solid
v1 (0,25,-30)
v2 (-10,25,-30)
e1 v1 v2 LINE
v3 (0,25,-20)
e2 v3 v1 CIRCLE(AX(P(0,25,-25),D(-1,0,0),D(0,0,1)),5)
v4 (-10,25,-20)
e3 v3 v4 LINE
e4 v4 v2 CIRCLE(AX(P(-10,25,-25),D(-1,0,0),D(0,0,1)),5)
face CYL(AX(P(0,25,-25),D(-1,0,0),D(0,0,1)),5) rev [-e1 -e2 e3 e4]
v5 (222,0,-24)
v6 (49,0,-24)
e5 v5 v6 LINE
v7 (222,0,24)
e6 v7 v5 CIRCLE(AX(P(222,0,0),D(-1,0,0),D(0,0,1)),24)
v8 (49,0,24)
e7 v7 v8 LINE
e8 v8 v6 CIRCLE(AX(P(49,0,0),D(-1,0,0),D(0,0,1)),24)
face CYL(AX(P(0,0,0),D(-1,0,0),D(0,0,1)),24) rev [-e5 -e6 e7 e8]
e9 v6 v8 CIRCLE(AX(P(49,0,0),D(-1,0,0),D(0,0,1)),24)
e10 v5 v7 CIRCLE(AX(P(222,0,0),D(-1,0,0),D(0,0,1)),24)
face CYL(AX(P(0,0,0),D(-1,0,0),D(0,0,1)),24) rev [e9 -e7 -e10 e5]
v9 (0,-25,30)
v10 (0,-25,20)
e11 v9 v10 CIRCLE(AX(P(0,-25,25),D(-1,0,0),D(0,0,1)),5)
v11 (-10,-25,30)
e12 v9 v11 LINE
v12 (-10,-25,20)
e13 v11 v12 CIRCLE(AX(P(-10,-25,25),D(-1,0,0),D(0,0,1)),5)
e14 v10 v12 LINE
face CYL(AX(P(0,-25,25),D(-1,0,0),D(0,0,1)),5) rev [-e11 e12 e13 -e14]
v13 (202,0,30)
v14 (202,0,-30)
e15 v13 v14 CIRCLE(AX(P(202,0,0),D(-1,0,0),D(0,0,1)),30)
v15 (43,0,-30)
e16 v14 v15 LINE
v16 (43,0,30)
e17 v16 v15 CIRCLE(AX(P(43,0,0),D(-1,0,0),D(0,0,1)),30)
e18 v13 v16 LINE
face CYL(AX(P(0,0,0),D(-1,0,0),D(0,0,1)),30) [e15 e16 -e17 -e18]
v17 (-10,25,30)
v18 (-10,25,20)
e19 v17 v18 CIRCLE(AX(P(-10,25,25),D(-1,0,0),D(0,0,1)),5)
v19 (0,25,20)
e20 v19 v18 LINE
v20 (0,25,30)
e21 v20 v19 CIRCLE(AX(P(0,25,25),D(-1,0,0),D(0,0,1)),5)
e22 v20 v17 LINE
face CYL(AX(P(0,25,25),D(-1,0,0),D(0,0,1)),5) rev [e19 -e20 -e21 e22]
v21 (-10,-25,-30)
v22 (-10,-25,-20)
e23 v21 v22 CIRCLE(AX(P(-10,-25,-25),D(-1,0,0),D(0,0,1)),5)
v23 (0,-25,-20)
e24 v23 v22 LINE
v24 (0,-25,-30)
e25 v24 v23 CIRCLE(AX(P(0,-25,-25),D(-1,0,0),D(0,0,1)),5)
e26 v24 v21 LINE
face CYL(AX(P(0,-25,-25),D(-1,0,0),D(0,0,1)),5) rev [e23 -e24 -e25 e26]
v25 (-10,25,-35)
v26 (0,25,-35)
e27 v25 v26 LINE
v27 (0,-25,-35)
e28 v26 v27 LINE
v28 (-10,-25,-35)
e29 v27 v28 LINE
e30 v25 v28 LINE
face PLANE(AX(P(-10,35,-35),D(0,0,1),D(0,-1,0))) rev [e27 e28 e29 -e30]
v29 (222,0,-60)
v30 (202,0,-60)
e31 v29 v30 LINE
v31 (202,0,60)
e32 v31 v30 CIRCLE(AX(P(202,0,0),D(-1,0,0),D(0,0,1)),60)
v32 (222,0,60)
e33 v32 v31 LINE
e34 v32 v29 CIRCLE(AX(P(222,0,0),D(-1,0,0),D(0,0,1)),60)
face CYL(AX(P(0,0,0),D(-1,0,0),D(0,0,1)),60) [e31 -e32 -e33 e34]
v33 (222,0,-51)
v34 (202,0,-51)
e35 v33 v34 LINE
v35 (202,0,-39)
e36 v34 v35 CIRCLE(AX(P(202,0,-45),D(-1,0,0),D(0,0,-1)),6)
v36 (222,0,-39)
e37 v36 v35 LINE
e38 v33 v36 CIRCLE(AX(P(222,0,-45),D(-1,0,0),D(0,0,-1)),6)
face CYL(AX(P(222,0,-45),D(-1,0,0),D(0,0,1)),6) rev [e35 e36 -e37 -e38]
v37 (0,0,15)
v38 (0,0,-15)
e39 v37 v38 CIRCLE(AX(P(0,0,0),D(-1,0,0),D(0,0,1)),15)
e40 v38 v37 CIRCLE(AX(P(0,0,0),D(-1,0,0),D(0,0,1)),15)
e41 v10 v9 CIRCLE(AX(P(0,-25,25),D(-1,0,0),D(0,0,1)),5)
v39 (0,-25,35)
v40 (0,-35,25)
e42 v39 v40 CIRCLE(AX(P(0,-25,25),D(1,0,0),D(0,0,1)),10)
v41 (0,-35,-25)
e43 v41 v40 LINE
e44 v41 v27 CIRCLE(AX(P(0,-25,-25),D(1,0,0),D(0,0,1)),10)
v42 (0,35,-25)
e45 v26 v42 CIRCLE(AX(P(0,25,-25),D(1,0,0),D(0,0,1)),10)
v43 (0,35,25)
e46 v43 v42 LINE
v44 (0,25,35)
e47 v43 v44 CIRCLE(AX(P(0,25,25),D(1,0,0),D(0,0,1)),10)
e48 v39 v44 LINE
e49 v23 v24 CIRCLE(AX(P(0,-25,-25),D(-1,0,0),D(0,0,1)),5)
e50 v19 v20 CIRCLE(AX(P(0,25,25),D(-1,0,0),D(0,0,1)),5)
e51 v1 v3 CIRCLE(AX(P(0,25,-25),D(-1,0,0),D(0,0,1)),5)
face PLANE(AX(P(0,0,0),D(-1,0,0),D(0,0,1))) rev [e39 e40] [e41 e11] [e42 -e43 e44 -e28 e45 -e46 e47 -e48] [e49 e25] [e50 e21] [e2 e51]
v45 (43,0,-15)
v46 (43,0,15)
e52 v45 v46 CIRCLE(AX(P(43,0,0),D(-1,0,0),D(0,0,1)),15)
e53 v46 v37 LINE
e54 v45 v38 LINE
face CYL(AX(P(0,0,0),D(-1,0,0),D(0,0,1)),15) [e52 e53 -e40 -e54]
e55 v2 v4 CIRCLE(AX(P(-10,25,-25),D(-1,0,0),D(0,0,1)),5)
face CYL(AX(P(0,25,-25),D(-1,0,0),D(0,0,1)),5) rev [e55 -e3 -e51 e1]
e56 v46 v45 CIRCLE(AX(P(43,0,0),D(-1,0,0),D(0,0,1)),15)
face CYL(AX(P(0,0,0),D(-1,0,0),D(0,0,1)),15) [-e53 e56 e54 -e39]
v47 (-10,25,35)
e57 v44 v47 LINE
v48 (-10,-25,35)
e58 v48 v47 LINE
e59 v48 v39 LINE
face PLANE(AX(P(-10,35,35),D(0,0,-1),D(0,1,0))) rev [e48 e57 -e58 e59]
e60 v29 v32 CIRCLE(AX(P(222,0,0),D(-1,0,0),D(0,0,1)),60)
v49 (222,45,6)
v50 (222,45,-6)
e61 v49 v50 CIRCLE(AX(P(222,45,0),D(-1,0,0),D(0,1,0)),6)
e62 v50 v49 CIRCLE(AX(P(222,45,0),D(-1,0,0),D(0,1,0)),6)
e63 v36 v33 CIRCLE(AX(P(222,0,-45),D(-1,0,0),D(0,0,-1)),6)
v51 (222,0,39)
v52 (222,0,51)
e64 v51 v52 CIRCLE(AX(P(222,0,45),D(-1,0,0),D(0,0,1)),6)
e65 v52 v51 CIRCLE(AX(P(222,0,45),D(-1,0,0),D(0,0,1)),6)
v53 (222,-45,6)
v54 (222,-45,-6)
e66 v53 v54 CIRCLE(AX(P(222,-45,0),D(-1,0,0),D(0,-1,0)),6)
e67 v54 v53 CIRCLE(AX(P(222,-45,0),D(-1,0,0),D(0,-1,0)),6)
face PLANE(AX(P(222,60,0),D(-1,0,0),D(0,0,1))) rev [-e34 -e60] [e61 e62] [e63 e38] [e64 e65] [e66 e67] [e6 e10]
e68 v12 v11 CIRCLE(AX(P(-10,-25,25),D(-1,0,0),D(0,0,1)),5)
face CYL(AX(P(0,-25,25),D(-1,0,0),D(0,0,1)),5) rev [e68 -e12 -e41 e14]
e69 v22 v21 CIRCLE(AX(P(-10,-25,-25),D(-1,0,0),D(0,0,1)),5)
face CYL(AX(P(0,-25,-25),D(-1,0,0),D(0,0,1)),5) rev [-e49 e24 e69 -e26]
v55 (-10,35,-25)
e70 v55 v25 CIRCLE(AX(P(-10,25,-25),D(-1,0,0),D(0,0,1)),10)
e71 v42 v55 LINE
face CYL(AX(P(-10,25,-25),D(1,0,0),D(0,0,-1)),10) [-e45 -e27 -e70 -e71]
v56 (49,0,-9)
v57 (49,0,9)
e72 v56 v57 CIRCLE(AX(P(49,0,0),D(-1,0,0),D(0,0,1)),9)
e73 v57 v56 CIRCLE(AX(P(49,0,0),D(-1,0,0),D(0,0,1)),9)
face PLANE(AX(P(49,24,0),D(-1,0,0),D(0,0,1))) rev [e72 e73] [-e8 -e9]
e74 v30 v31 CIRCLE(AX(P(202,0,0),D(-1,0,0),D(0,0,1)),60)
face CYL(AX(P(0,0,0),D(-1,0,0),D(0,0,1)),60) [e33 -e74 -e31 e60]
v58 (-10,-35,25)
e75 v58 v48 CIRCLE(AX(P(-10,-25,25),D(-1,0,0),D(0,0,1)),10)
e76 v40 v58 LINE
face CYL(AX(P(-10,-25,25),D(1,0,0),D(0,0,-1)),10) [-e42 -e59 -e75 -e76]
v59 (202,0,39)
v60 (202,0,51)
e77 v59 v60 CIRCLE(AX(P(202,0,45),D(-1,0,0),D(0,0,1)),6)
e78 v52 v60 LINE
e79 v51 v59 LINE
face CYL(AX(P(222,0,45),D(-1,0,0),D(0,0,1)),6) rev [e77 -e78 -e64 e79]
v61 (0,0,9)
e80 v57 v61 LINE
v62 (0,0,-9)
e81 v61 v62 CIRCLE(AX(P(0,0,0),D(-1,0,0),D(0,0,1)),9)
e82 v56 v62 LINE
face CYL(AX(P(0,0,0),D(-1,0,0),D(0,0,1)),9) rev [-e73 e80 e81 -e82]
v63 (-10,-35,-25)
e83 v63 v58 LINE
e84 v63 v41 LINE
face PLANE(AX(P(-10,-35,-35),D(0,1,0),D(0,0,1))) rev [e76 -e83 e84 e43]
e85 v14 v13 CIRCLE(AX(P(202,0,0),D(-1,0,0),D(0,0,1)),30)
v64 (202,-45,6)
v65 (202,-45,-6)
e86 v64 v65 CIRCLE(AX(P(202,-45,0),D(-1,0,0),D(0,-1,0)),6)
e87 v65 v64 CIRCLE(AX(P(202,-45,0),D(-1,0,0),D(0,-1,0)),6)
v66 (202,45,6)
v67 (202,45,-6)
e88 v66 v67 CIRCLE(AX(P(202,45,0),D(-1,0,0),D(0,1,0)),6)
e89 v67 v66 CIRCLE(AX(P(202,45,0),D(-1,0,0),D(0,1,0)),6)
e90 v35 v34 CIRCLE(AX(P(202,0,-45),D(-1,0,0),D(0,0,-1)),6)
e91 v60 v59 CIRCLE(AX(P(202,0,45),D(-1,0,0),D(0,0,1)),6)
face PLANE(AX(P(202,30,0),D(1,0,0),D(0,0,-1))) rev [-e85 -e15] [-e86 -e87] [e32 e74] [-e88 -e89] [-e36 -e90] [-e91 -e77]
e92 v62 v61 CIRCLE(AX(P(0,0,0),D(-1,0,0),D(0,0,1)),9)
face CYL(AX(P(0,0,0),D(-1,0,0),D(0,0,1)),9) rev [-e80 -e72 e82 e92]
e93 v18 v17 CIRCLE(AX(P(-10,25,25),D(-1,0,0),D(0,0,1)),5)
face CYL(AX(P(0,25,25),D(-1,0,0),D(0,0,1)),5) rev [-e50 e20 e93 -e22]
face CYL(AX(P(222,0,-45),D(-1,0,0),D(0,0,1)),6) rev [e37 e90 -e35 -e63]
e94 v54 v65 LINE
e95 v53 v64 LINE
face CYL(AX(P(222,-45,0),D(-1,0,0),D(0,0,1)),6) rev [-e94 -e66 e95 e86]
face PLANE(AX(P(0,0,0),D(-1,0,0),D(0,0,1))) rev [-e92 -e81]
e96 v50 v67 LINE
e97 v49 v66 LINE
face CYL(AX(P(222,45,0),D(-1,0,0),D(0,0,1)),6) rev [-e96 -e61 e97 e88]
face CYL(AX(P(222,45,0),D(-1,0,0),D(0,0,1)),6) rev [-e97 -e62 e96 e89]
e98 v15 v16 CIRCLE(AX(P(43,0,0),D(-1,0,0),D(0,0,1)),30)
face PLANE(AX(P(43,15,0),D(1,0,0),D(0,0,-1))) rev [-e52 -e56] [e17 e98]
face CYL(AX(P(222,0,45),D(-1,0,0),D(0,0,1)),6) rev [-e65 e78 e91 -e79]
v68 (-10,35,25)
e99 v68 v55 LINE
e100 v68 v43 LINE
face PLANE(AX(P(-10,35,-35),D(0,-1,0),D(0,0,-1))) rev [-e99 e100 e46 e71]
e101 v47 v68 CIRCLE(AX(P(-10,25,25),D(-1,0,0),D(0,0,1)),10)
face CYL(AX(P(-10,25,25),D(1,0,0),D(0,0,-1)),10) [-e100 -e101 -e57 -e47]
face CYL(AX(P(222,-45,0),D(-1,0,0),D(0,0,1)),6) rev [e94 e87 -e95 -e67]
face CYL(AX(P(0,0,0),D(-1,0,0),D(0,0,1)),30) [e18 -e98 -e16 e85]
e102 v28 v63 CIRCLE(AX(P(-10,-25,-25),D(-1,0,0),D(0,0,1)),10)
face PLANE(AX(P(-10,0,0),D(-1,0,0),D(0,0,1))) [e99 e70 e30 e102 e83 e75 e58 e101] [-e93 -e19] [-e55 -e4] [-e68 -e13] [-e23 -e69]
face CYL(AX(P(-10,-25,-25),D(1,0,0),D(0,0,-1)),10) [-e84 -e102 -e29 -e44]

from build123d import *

# Parameters (mm, degrees)
SQUARE_FLANGE_SKETCH_70X70_W            = 70
SQUARE_FLANGE_SKETCH_70X70_H            = 70
SQUARE_MOUNTING_FLANGE_DEPTH            = 10
SQUARE_FLANGE_CORNER_FILLETS_R10_R      = 10
SQUARE_FLANGE_HOLES_SKETCH_R            = 5
SQUARE_FLANGE_MOUNTING_HOLES_4X_DEPTH   = 10
ROUND_FLANGE_HOLE_SKETCH_R              = 6
ROUND_FLANGE_BOLT_HOLE_12_DEPTH         = 229.350607619
ROUND_FLANGE_BOLT_HOLE_PATTERN_4X_COUNT = 4


with BuildPart() as part:
    # Housing Profile Sketch → Housing Body Revolve (revolve)
    with BuildSketch(Plane.XY, mode=Mode.PRIVATE) as housing_body_revolve_sk:
        Polygon((0, 15), (43, 15), (43, 30), (202, 30), (202, 60), (222, 60), (222, 24), (49, 24), (49, 9), (0, 9), align=None)
    revolve(housing_body_revolve_sk.sketch.rotate(Axis((0, 0, 0), (1, 0, 0)), 90), axis=Axis((0, 0, 0), (1, 0, 0)))

    # Square Flange Sketch 70x70 → Square Mounting Flange (add)
    with BuildSketch(Plane.ZY):
        Rectangle(SQUARE_FLANGE_SKETCH_70X70_W, SQUARE_FLANGE_SKETCH_70X70_H)
    extrude(amount=SQUARE_MOUNTING_FLANGE_DEPTH)

    # Square Flange Corner Fillets R10
    square_flange_corner_fillets_r10_edges = [part.edges().sort_by_distance(p)[0] for p in [
        (-5, -35, 35),
        (-5, 35, 35),
        (-5, 35, -35),
        (-5, -35, -35),
    ]]
    fillet(square_flange_corner_fillets_r10_edges, radius=SQUARE_FLANGE_CORNER_FILLETS_R10_R)

    # Square Flange Holes Sketch → Square Flange Mounting Holes 4x (cut)
    with BuildSketch(Plane.ZY.offset(10)):
        with Locations((25, 25)):
            Circle(SQUARE_FLANGE_HOLES_SKETCH_R)
        with Locations((-25, 25)):
            Circle(SQUARE_FLANGE_HOLES_SKETCH_R)
        with Locations((-25, -25)):
            Circle(SQUARE_FLANGE_HOLES_SKETCH_R)
        with Locations((25, -25)):
            Circle(SQUARE_FLANGE_HOLES_SKETCH_R)
    extrude(amount=-SQUARE_FLANGE_MOUNTING_HOLES_4X_DEPTH, mode=Mode.SUBTRACT)

    # Round Flange Hole Sketch → Round Flange Bolt Hole Ø12 (cut, through all)
    with BuildSketch(Plane.ZY.offset(-202)):
        with Locations((45, 0)):
            Circle(ROUND_FLANGE_HOLE_SKETCH_R)
    round_flange_bolt_hole_12 = extrude(amount=-ROUND_FLANGE_BOLT_HOLE_12_DEPTH, mode=Mode.SUBTRACT)

    # Round Flange Bolt Hole Pattern 4x: Round Flange Bolt Hole Ø12 ×4 about axis
    round_flange_bolt_hole_pattern_4x_axis = Axis((0, 0, 0), (1, 0, 0))
    for i in range(1, ROUND_FLANGE_BOLT_HOLE_PATTERN_4X_COUNT):
        add(round_flange_bolt_hole_12.rotate(round_flange_bolt_hole_pattern_4x_axis, i * 360 / ROUND_FLANGE_BOLT_HOLE_PATTERN_4X_COUNT), mode=Mode.SUBTRACT)


solid = part.part
